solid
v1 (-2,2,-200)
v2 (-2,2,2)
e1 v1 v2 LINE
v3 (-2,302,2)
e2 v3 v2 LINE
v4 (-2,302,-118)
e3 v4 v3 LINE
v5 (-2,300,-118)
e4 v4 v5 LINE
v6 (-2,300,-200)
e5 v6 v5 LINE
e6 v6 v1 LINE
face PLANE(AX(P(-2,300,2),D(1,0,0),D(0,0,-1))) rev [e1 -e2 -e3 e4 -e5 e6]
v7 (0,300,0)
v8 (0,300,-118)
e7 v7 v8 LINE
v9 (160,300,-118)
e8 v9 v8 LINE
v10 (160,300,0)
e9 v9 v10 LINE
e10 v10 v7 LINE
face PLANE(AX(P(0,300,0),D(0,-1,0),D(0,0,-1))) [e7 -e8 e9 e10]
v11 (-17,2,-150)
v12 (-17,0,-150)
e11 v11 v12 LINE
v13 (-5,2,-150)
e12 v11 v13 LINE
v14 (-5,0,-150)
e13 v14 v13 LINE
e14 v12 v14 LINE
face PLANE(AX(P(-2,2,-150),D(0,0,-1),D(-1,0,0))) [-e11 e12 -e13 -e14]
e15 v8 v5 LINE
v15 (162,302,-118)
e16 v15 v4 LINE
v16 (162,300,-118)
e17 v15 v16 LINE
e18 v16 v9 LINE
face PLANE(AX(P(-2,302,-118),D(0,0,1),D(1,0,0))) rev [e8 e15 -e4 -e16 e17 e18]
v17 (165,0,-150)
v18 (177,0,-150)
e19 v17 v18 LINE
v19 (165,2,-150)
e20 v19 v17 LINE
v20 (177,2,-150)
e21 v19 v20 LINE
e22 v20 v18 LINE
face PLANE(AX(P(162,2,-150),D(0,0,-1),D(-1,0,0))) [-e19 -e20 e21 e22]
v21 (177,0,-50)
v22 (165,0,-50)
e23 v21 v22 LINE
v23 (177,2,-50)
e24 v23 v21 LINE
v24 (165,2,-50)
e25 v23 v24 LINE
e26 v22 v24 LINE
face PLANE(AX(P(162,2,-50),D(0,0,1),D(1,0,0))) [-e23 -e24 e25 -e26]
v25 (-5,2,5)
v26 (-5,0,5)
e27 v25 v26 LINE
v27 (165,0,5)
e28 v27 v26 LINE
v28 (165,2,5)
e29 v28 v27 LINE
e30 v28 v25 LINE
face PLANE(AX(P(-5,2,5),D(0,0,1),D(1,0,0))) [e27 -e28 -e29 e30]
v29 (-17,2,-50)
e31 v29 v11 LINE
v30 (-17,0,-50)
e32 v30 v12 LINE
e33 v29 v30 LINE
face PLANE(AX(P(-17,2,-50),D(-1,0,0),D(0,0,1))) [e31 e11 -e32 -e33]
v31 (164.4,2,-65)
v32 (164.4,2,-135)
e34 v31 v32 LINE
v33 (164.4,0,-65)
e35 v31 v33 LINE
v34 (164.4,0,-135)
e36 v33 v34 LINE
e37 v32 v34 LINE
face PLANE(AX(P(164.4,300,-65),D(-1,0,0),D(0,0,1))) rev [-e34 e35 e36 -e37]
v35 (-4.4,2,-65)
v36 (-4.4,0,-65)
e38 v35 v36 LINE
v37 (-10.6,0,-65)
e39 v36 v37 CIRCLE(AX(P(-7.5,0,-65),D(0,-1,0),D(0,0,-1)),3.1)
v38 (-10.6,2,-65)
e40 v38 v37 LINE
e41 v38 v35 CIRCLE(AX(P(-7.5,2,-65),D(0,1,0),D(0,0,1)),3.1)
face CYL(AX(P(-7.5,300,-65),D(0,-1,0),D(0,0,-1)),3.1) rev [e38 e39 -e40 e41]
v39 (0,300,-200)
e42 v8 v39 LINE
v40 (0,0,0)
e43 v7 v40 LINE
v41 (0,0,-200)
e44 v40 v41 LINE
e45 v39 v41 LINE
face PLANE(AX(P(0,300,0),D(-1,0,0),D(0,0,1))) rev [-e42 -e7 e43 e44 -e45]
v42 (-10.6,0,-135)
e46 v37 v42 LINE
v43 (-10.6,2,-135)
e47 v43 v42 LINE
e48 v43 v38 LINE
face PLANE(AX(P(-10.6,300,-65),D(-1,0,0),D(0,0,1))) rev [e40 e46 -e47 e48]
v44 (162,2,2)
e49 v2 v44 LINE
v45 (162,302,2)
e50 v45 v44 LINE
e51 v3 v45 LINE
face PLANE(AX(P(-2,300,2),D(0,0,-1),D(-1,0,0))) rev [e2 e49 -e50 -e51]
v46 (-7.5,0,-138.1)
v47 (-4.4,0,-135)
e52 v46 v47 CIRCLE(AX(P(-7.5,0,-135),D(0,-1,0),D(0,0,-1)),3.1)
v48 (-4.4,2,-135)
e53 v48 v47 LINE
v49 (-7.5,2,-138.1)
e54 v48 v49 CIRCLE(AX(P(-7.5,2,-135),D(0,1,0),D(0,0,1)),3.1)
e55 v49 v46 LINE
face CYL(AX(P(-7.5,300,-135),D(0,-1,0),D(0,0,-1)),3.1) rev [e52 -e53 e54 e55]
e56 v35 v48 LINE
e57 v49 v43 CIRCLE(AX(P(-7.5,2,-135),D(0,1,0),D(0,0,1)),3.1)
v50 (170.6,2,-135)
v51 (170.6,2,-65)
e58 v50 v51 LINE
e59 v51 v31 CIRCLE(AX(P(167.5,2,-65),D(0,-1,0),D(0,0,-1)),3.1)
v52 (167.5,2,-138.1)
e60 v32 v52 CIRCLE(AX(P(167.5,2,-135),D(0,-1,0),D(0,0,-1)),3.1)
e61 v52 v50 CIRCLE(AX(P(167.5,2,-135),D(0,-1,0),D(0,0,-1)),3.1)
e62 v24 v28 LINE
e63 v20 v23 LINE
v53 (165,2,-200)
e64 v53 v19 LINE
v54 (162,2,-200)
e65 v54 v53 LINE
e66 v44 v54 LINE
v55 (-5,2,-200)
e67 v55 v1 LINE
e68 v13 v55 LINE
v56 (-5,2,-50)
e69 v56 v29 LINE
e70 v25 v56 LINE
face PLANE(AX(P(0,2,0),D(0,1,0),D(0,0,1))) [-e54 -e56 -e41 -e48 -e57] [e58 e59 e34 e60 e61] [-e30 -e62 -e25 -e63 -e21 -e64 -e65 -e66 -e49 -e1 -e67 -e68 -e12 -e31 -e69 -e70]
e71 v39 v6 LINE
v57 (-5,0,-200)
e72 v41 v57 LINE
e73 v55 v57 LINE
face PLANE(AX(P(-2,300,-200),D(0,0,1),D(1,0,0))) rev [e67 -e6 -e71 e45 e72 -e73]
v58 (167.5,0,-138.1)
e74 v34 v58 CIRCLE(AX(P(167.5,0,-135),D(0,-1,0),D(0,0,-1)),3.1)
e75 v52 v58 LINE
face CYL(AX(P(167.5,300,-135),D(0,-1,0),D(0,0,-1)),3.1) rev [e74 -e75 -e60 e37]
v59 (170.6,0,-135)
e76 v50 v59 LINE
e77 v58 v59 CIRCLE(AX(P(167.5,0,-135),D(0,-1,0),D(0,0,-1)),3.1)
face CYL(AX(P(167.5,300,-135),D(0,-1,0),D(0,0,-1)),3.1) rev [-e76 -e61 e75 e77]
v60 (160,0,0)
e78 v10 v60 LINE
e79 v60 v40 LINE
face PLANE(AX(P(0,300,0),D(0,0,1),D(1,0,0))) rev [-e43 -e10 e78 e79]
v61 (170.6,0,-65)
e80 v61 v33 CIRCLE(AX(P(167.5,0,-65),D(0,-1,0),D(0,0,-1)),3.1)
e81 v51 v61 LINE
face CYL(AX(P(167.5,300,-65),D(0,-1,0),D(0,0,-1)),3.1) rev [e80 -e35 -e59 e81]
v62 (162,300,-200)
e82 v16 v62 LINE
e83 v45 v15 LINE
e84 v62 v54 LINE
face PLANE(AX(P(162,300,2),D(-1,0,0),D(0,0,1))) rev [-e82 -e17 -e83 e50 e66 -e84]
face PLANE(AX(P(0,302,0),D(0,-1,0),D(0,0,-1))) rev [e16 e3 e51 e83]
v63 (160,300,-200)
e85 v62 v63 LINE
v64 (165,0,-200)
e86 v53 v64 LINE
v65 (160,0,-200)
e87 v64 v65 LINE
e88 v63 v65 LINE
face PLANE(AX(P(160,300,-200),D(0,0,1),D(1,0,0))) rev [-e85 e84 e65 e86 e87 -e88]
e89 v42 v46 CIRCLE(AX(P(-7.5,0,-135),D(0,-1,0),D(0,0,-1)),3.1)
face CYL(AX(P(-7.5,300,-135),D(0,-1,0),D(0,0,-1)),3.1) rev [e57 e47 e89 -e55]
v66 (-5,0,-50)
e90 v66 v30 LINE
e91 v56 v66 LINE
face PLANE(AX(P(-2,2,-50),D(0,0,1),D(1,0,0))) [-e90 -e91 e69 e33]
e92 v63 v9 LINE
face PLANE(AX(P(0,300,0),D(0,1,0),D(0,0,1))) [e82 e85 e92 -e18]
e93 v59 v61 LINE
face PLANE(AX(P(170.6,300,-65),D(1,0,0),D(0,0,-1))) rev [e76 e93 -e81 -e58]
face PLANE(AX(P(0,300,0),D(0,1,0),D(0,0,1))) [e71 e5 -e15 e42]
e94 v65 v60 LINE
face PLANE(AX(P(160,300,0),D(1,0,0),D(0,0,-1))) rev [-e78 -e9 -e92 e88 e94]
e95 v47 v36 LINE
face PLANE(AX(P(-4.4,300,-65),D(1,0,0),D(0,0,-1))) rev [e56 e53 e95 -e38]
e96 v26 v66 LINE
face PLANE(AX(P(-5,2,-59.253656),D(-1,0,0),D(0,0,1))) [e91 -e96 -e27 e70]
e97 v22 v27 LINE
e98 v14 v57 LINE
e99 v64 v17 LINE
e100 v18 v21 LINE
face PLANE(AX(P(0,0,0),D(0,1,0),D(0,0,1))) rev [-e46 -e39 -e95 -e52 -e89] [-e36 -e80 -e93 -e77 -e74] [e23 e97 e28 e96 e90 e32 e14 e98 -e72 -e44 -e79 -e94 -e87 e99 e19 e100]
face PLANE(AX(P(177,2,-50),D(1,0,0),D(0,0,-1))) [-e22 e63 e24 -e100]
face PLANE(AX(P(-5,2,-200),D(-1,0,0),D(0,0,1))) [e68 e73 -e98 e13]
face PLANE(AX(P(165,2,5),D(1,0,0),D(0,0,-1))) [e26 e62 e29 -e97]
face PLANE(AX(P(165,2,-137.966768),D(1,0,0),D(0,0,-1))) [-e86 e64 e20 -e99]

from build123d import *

# Parameters (mm, degrees)
BOSS_EXTRUDE1_DEPTH     = 300
SKETCH4_W               = 15
SKETCH4_H               = 100
BOSS_EXTRUDE3_DEPTH     = 2
CUT_EXTRUDE2_DEPTH      = 402.657814564
CUT_EXTRUDE2_DEPTH_BACK = 402.657814564
SKETCH6_W               = 164
SKETCH6_H               = 120
BOSS_EXTRUDE4_DEPTH     = 2
BOSS_EXTRUDE5_DEPTH     = 2


with BuildPart() as part:
    # Sketch1 → Boss-Extrude1 (new body)
    with BuildSketch(Plane(origin=(0, 0, 0), x_dir=(1, 0, 0), z_dir=(0, 1, 0))):
        Polygon((160, 0), (160, 200), (162, 200), (162, -2), (-2, -2), (-2, 200), (0, 200), (0, 0), align=None)
    extrude(amount=BOSS_EXTRUDE1_DEPTH)

    # Sketch4 → Boss-Extrude3 (add)
    with BuildSketch(Plane.XZ):
        with Locations((-9.5, -100)):
            Rectangle(SKETCH4_W, SKETCH4_H)
        with Locations((169.5, -100)):
            Rectangle(SKETCH4_W, SKETCH4_H)
    extrude(amount=-BOSS_EXTRUDE3_DEPTH)

    # Sketch5 → Cut-Extrude2 (cut, two sides: drawn at the far end of the back side and taken through both)
    with BuildSketch(Plane.XZ.offset(-CUT_EXTRUDE2_DEPTH_BACK)):
        with BuildLine():
            Line((-4.4, -65), (-4.4, -135))
            ThreePointArc((-4.4, -135), (-7.5, -138.1), (-10.6, -135))
            Line((-10.6, -135), (-10.6, -65))
            ThreePointArc((-10.6, -65), (-7.5, -61.9), (-4.4, -65))
        make_face()
        with BuildLine():
            Line((170.6, -65), (170.6, -135))
            ThreePointArc((170.6, -135), (167.5, -138.1), (164.4, -135))
            Line((164.4, -135), (164.4, -65))
            ThreePointArc((164.4, -65), (167.5, -61.9), (170.6, -65))
        make_face()
    extrude(amount=CUT_EXTRUDE2_DEPTH + CUT_EXTRUDE2_DEPTH_BACK, mode=Mode.SUBTRACT)

    # Sketch6 → Boss-Extrude4 (add)
    with BuildSketch(Plane(origin=(0, 300, 0), x_dir=(1, 0, 0), z_dir=(0, 1, 0))):
        with Locations((80, 58)):
            Rectangle(SKETCH6_W, SKETCH6_H)
    extrude(amount=BOSS_EXTRUDE4_DEPTH)

    # Sketch7 → Boss-Extrude5 (add)
    with BuildSketch(Plane.XZ):
        Polygon((-2, -200), (-2, 2), (162, 2), (162, -200), (165, -200), (165, -137.966768061), (163.387303915, -137.966768061), (163.387303915, -56.304675841), (165, -56.304675841), (165, 5), (-5, 5), (-5, -59.253655593), (-3.5, -59.253655593), (-3.5, -137.966768061), (-5, -137.966768061), (-5, -200), align=None)
    extrude(amount=-BOSS_EXTRUDE5_DEPTH)


solid = part.part
